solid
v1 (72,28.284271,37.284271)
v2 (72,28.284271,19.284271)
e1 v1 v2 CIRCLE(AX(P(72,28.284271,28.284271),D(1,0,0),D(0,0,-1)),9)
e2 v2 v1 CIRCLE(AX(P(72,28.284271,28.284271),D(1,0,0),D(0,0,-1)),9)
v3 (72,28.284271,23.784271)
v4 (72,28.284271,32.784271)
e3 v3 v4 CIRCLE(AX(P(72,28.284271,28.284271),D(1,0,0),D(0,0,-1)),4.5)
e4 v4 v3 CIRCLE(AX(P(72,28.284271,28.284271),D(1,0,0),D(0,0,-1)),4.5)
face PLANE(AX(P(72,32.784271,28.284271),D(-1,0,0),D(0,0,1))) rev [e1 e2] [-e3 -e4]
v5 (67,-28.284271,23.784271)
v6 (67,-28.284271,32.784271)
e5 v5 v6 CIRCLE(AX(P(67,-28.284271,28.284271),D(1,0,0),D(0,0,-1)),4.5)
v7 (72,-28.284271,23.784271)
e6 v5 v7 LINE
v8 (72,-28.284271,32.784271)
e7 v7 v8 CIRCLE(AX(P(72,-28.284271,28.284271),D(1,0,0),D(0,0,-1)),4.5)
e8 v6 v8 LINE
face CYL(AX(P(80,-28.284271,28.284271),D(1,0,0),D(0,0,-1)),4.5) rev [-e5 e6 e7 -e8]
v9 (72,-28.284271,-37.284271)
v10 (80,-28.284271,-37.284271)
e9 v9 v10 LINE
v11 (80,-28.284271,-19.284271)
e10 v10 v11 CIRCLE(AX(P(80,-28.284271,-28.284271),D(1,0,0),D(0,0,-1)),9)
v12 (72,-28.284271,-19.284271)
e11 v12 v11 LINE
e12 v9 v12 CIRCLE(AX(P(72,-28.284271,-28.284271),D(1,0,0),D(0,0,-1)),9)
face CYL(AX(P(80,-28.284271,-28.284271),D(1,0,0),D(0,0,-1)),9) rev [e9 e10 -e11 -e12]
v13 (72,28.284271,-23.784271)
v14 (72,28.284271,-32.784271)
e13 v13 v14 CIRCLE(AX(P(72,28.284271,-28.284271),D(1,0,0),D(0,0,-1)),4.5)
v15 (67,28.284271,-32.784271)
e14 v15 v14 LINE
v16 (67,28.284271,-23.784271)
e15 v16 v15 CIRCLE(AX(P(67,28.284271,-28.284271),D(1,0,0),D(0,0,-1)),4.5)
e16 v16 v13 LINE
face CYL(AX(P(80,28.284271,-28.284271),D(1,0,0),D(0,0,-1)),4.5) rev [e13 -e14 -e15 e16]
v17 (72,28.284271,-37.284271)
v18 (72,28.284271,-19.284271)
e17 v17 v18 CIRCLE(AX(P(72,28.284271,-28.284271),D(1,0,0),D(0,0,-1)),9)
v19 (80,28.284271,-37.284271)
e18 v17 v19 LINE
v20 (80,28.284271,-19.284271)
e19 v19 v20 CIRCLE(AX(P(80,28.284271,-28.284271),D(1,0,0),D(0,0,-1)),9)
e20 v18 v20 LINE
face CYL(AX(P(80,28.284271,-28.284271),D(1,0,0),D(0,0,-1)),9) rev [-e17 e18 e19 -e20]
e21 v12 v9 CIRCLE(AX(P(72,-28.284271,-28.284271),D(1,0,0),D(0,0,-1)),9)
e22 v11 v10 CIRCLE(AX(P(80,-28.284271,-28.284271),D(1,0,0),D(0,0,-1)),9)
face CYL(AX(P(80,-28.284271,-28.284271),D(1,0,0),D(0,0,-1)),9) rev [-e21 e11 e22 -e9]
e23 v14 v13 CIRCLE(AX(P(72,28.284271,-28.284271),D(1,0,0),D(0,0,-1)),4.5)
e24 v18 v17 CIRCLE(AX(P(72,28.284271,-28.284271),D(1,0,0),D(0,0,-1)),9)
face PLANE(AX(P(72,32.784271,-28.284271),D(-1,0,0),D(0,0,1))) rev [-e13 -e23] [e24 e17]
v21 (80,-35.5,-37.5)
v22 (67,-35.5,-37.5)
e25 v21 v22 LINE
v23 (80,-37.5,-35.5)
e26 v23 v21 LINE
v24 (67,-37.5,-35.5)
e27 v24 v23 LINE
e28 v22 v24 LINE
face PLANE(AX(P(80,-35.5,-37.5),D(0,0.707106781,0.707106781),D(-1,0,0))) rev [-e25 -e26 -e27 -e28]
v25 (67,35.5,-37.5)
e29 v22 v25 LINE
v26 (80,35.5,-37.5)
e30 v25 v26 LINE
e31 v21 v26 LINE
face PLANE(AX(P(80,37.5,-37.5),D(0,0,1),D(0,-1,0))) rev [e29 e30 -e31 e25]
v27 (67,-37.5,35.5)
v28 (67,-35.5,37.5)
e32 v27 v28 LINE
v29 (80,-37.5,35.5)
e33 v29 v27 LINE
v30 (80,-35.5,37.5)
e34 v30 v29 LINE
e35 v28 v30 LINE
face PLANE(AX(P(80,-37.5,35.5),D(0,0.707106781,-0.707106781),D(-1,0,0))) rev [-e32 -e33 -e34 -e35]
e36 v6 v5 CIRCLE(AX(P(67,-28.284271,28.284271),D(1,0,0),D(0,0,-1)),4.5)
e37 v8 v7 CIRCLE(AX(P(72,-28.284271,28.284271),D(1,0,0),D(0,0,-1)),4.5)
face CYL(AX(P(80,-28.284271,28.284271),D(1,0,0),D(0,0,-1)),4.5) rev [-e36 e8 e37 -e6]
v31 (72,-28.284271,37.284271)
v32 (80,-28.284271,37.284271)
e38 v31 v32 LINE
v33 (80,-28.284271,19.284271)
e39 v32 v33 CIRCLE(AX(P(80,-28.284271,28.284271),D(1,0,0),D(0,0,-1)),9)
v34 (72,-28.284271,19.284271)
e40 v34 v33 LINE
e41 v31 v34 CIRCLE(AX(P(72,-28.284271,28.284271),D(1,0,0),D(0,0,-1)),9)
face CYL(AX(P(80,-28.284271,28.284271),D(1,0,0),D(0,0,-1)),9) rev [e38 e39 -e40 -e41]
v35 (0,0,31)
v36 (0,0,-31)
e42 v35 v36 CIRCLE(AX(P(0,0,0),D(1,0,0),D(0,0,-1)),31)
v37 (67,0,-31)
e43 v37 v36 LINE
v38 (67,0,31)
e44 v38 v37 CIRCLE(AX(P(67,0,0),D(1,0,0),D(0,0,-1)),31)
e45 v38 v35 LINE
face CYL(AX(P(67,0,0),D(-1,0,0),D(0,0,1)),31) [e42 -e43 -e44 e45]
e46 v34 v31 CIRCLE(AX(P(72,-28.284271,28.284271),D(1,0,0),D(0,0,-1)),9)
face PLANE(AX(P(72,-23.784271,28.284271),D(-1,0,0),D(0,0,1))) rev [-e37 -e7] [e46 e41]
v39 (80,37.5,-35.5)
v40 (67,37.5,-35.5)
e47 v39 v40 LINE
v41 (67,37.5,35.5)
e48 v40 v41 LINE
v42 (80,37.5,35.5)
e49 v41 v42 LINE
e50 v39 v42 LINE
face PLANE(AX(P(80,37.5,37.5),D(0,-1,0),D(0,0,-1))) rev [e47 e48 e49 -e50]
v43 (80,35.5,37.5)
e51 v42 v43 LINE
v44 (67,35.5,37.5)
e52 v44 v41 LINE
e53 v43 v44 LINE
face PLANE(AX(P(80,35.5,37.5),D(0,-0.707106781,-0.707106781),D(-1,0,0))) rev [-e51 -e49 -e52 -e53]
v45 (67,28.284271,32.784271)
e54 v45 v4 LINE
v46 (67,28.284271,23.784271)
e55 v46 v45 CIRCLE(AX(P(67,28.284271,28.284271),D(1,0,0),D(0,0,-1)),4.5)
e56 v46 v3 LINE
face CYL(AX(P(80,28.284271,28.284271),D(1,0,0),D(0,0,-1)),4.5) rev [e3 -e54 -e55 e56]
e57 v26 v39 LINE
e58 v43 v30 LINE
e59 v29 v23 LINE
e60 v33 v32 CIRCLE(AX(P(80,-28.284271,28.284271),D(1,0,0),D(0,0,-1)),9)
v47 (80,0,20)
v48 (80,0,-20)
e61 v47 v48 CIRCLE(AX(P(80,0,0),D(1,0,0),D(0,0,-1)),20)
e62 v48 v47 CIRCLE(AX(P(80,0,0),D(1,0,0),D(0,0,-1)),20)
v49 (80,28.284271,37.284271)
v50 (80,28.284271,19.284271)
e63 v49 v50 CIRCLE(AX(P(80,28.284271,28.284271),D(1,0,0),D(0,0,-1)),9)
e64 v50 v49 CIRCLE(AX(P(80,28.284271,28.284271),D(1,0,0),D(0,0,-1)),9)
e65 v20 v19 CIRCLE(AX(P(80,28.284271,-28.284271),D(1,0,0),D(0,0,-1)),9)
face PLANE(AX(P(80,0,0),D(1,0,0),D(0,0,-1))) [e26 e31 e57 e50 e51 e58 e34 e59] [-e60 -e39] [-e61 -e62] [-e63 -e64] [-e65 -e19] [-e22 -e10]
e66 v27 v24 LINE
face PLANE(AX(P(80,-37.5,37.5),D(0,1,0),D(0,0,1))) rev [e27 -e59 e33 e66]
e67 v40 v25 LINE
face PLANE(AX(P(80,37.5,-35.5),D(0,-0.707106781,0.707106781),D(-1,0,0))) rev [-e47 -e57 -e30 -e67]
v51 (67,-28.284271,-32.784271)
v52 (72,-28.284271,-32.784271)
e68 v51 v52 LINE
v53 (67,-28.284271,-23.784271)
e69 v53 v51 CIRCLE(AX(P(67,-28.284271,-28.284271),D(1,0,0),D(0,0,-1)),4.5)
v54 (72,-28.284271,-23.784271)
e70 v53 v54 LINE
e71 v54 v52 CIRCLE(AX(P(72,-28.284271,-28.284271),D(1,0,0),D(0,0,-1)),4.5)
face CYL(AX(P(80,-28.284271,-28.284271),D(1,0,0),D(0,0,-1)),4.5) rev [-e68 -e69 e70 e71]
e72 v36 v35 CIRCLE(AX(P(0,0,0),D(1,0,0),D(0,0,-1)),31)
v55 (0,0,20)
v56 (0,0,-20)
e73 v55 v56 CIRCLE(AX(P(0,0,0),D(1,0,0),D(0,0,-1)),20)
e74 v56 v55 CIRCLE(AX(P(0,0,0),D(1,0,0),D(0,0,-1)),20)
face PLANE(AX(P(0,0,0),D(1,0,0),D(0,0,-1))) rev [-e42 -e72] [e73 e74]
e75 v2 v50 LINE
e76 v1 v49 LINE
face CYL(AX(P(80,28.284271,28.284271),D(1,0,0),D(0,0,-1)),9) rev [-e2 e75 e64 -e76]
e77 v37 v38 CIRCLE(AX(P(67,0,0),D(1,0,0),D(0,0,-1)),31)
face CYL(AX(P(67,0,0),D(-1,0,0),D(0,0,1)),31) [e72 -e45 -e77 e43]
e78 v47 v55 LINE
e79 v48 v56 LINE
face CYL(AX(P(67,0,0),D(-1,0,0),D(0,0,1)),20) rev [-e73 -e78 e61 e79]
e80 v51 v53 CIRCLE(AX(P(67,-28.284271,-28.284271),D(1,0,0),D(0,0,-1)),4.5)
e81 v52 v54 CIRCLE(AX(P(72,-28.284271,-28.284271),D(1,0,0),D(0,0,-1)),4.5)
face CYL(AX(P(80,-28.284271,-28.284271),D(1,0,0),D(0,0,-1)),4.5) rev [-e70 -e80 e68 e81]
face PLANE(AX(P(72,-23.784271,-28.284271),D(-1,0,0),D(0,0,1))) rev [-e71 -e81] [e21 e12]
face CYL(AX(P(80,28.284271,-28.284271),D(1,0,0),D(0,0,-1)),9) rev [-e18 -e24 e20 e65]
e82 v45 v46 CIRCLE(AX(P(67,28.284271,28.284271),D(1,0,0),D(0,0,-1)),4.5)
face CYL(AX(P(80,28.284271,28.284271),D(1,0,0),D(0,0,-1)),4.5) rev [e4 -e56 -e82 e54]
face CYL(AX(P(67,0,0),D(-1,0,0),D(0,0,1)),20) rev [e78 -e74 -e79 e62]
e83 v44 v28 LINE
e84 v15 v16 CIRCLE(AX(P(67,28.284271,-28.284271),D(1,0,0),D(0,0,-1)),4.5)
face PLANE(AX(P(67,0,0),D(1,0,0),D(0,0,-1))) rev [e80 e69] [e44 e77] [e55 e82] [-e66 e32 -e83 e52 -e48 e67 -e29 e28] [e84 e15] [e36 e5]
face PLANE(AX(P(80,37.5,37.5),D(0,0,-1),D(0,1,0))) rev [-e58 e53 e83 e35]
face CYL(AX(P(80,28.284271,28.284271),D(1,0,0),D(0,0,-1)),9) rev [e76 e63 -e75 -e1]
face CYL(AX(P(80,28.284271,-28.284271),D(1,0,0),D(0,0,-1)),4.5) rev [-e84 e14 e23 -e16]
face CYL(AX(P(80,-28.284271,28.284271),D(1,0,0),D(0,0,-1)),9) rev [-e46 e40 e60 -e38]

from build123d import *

# Parameters (mm, degrees)
SKETCH1_R                               = 31
SKETCH1_R_2                             = 20
BOSS_EXTRUDE1_DEPTH                     = 67
SKETCH2_W                               = 75
SKETCH2_H                               = 75
SKETCH2_R                               = 20
BOSS_EXTRUDE2_DEPTH                     = 13
CBORE_FOR_M8_HEX_HEAD_BOLT1_D           = 9
CBORE_FOR_M8_HEX_HEAD_BOLT1_CBORE_D     = 18
CBORE_FOR_M8_HEX_HEAD_BOLT1_CBORE_DEPTH = 8
CHAMFER1_SIZE                           = 2


with BuildPart() as part:
    # Sketch1 → Boss-Extrude1 (new body)
    with BuildSketch(Plane(origin=(0, 0, 0), x_dir=(0, 0, -1), z_dir=(1, 0, 0))):
        Circle(SKETCH1_R)
        Circle(SKETCH1_R_2, mode=Mode.SUBTRACT)
    extrude(amount=BOSS_EXTRUDE1_DEPTH)

    # Sketch2 → Boss-Extrude2 (add)
    with BuildSketch(Plane(origin=(67, 0, 0), x_dir=(0, 0, -1), z_dir=(1, 0, 0))):
        Rectangle(SKETCH2_W, SKETCH2_H)
        Circle(SKETCH2_R, mode=Mode.SUBTRACT)
    extrude(amount=BOSS_EXTRUDE2_DEPTH)

    # CBORE for M8 Hex Head Bolt1 (through all)
    with Locations(Plane(origin=(80, 0, 0), x_dir=(0, 0, -1), z_dir=(1, 0, 0))):
        with Locations((28.284271247, 28.284271247), (28.284271247, -28.284271247), (-28.284271247, -28.284271247), (-28.284271247, 28.284271247)):
            CounterBoreHole(CBORE_FOR_M8_HEX_HEAD_BOLT1_D / 2, CBORE_FOR_M8_HEX_HEAD_BOLT1_CBORE_D / 2, CBORE_FOR_M8_HEX_HEAD_BOLT1_CBORE_DEPTH)

    # Chamfer1
    chamfer1_edges = [part.edges().sort_by_distance(p)[0] for p in [
        (73.5, -37.5, -37.5),
        (73.5, 37.5, -37.5),
        (73.5, 37.5, 37.5),
        (73.5, -37.5, 37.5),
    ]]
    chamfer(chamfer1_edges, length=CHAMFER1_SIZE)


solid = part.part
